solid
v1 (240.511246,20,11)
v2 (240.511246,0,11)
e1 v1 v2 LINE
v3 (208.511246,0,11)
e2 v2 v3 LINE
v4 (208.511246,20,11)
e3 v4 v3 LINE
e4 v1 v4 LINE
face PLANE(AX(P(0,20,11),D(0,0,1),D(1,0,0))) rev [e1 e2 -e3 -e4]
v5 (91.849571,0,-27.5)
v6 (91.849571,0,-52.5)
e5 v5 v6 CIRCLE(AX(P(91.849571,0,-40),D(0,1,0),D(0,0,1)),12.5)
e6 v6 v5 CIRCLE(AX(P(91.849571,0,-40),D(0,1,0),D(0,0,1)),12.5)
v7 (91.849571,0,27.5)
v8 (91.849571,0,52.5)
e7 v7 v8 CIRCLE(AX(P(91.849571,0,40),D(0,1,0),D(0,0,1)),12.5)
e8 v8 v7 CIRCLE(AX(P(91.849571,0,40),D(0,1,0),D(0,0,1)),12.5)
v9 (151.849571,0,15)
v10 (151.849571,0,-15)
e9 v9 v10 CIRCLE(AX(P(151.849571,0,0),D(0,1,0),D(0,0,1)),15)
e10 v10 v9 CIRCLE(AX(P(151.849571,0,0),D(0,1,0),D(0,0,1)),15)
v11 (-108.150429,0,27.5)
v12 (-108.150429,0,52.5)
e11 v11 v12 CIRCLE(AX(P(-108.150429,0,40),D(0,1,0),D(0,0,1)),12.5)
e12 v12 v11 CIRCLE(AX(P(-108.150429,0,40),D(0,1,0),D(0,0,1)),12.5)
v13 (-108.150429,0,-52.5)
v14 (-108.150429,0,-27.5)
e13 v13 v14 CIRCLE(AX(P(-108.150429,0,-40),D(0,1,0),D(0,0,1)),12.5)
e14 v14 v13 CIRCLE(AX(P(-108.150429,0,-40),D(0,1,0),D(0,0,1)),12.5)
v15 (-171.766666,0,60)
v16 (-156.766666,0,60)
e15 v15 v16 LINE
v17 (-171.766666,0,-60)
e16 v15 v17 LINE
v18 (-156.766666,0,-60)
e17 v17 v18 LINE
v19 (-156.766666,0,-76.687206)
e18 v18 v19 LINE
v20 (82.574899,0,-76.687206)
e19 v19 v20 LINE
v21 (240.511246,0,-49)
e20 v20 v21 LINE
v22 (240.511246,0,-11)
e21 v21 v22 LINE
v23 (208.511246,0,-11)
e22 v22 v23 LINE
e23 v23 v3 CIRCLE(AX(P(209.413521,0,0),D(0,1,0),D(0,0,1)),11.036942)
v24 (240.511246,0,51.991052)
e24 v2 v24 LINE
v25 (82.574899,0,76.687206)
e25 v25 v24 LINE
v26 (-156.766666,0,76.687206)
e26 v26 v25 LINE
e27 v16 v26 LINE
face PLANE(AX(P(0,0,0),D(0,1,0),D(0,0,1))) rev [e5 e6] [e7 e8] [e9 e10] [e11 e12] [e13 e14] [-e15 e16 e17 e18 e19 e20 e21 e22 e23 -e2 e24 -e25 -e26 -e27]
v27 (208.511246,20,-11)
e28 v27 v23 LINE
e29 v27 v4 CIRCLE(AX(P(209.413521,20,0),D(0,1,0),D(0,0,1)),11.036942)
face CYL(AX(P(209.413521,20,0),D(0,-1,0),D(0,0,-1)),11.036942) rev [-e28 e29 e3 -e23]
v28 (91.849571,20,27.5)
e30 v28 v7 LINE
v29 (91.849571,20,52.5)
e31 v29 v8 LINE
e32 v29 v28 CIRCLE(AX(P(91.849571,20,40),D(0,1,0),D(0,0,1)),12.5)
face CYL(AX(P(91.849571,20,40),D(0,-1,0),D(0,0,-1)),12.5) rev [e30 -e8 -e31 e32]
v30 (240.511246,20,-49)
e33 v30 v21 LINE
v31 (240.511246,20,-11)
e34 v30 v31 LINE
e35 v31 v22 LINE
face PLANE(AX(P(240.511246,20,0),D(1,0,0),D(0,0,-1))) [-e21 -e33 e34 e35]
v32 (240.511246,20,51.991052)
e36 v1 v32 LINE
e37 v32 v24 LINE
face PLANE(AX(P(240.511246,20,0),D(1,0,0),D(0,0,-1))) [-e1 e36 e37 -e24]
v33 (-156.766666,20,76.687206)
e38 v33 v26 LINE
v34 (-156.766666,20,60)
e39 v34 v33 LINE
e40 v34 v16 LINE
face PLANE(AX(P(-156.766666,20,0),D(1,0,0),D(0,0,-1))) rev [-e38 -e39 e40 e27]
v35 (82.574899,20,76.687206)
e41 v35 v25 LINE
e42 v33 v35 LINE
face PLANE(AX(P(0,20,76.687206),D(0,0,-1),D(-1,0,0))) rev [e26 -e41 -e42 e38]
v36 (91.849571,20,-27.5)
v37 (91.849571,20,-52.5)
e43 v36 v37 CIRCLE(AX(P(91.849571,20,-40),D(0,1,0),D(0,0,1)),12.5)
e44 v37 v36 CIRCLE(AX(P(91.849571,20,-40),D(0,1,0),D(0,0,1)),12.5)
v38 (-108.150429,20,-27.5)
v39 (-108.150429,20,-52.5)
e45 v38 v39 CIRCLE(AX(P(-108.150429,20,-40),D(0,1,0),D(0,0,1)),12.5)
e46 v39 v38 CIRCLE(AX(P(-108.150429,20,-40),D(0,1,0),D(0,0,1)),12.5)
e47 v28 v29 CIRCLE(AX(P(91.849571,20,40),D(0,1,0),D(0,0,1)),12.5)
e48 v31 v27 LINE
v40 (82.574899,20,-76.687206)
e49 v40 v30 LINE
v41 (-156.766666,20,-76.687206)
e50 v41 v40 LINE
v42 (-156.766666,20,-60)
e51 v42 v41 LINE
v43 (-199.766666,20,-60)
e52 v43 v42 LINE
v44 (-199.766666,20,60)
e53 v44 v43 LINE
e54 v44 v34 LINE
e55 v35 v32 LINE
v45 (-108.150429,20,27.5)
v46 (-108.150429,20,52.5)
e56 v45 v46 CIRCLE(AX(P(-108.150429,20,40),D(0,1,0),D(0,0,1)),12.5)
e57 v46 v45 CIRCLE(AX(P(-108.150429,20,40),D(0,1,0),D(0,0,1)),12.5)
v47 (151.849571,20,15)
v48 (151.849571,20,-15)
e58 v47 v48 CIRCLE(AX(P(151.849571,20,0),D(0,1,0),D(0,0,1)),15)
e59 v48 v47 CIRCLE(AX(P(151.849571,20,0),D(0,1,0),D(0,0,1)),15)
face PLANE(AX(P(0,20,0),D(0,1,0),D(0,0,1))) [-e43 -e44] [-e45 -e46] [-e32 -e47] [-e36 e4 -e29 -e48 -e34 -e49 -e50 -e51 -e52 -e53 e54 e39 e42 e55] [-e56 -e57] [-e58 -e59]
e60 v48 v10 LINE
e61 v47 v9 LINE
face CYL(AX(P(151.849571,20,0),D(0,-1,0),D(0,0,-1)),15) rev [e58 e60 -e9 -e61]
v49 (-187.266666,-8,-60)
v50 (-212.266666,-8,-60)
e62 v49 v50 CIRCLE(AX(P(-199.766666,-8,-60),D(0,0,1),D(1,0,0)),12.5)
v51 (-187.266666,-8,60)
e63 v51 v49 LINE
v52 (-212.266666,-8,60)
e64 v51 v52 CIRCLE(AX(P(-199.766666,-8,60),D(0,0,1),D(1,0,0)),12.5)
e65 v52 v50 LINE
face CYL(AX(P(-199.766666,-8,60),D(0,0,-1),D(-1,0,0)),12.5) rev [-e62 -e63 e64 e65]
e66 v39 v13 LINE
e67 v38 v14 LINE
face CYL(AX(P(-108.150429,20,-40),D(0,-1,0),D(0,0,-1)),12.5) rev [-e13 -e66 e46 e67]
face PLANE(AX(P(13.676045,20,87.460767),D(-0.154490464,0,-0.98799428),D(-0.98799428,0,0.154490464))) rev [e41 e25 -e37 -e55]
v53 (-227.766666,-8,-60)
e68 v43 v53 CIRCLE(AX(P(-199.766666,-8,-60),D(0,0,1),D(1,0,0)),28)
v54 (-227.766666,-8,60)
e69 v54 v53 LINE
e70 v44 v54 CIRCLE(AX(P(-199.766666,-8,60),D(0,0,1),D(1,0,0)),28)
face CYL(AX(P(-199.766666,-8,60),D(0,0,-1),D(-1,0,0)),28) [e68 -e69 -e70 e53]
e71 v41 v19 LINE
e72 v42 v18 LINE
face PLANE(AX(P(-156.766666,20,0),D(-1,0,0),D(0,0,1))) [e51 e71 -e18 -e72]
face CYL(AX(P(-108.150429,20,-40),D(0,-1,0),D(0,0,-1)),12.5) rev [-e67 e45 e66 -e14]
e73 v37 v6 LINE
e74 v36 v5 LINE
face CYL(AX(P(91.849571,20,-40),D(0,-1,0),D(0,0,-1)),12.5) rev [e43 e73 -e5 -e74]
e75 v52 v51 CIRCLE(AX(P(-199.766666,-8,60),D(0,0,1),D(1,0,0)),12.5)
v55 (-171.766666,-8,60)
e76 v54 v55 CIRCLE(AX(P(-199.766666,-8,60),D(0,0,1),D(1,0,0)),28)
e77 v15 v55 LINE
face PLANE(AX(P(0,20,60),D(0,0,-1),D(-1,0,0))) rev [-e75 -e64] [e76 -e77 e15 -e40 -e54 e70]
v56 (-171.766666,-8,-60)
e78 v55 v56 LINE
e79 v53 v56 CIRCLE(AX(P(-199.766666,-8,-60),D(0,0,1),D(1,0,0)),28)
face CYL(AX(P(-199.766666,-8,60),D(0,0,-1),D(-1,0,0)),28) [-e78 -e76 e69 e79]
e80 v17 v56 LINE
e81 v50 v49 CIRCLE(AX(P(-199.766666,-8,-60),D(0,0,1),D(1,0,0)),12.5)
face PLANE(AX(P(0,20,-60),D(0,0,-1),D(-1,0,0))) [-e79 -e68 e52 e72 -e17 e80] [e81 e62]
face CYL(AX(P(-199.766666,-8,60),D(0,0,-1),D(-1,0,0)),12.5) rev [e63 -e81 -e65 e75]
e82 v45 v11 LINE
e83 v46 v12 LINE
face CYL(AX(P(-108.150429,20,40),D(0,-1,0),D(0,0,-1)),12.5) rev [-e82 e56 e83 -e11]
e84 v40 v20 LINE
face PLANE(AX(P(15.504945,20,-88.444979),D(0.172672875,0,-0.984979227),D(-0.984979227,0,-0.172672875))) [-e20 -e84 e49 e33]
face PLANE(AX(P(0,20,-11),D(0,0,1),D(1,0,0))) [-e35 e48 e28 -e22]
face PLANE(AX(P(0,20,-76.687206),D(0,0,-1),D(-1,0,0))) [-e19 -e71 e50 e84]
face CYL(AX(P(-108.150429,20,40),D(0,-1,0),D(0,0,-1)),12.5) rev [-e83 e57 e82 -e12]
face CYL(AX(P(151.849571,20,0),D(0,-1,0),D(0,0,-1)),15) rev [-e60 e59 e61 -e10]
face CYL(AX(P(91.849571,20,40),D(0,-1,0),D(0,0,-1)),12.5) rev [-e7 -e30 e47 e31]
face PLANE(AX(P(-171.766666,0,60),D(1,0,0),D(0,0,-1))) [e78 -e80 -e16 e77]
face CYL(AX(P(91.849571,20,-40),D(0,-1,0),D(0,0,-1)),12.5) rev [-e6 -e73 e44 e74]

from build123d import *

# Parameters (mm, degrees)
SKETCH1_R           = 12.5
SKETCH1_R_2         = 15
BOSS_EXTRUDE1_DEPTH = 20
SKETCH2_R           = 12.5
BOSS_EXTRUDE3_DEPTH = 60


with BuildPart() as part:
    # Sketch1 → Boss-Extrude1 (new body)
    with BuildSketch(Plane(origin=(0, 0, 0), x_dir=(1, 0, 0), z_dir=(0, 1, 0))):
        with BuildLine():
            Line((-156.766665721, -76.687206232), (82.57489949, -76.687206232))
            Line((82.57489949, -76.687206232), (240.511245974, -51.99105161))
            Line((240.511245974, -51.99105161), (240.511245974, -11))
            Line((240.511245974, -11), (208.511245974, -11))
            ThreePointArc((208.511245974, -11), (198.376578208, 0), (208.511245974, 11))
            Line((208.511245974, 11), (240.511245974, 11))
            Line((240.511245974, 11), (240.511245974, 49))
            Line((240.511245974, 49), (82.57489949, 76.687206232))
            Line((82.57489949, 76.687206232), (-156.766665721, 76.687206232))
            Line((-156.766665721, 76.687206232), (-156.766665721, 60))
            Line((-156.766665721, 60), (-171.766665721, 60))
            Line((-171.766665721, 60), (-171.766665721, -60))
            Line((-171.766665721, -60), (-156.766665721, -60))
            Line((-156.766665721, -60), (-156.766665721, -76.687206232))
        make_face()
        with Locations(Location((-108.150428542, 40, 0), (0, 0, 270))):
            Circle(SKETCH1_R, mode=Mode.SUBTRACT)
        with Locations(Location((-108.150428542, -40, 0), (0, 0, 270))):
            Circle(SKETCH1_R, mode=Mode.SUBTRACT)
        with Locations(Location((91.849571458, 40, 0), (0, 0, 270))):
            Circle(SKETCH1_R, mode=Mode.SUBTRACT)
        with Locations(Location((91.849571458, -40, 0), (0, 0, 270))):
            Circle(SKETCH1_R, mode=Mode.SUBTRACT)
        with Locations(Location((151.849571458, 0, 0), (0, 0, 270))):
            Circle(SKETCH1_R_2, mode=Mode.SUBTRACT)
    extrude(amount=BOSS_EXTRUDE1_DEPTH)

    # Sketch2 → Boss-Extrude3 (add, symmetric)
    with BuildSketch(Plane.XY):
        with BuildLine():
            Line((-199.766665721, 20), (-171.766665721, 20))
            Line((-171.766665721, 20), (-171.766665721, -8))
            ThreePointArc((-171.766665721, -8), (-219.565655594, -27.798989873), (-199.766665721, 20))
        make_face()
        with Locations((-199.766665721, -8)):
            Circle(SKETCH2_R, mode=Mode.SUBTRACT)
    extrude(amount=BOSS_EXTRUDE3_DEPTH, both=True)


solid = part.part
